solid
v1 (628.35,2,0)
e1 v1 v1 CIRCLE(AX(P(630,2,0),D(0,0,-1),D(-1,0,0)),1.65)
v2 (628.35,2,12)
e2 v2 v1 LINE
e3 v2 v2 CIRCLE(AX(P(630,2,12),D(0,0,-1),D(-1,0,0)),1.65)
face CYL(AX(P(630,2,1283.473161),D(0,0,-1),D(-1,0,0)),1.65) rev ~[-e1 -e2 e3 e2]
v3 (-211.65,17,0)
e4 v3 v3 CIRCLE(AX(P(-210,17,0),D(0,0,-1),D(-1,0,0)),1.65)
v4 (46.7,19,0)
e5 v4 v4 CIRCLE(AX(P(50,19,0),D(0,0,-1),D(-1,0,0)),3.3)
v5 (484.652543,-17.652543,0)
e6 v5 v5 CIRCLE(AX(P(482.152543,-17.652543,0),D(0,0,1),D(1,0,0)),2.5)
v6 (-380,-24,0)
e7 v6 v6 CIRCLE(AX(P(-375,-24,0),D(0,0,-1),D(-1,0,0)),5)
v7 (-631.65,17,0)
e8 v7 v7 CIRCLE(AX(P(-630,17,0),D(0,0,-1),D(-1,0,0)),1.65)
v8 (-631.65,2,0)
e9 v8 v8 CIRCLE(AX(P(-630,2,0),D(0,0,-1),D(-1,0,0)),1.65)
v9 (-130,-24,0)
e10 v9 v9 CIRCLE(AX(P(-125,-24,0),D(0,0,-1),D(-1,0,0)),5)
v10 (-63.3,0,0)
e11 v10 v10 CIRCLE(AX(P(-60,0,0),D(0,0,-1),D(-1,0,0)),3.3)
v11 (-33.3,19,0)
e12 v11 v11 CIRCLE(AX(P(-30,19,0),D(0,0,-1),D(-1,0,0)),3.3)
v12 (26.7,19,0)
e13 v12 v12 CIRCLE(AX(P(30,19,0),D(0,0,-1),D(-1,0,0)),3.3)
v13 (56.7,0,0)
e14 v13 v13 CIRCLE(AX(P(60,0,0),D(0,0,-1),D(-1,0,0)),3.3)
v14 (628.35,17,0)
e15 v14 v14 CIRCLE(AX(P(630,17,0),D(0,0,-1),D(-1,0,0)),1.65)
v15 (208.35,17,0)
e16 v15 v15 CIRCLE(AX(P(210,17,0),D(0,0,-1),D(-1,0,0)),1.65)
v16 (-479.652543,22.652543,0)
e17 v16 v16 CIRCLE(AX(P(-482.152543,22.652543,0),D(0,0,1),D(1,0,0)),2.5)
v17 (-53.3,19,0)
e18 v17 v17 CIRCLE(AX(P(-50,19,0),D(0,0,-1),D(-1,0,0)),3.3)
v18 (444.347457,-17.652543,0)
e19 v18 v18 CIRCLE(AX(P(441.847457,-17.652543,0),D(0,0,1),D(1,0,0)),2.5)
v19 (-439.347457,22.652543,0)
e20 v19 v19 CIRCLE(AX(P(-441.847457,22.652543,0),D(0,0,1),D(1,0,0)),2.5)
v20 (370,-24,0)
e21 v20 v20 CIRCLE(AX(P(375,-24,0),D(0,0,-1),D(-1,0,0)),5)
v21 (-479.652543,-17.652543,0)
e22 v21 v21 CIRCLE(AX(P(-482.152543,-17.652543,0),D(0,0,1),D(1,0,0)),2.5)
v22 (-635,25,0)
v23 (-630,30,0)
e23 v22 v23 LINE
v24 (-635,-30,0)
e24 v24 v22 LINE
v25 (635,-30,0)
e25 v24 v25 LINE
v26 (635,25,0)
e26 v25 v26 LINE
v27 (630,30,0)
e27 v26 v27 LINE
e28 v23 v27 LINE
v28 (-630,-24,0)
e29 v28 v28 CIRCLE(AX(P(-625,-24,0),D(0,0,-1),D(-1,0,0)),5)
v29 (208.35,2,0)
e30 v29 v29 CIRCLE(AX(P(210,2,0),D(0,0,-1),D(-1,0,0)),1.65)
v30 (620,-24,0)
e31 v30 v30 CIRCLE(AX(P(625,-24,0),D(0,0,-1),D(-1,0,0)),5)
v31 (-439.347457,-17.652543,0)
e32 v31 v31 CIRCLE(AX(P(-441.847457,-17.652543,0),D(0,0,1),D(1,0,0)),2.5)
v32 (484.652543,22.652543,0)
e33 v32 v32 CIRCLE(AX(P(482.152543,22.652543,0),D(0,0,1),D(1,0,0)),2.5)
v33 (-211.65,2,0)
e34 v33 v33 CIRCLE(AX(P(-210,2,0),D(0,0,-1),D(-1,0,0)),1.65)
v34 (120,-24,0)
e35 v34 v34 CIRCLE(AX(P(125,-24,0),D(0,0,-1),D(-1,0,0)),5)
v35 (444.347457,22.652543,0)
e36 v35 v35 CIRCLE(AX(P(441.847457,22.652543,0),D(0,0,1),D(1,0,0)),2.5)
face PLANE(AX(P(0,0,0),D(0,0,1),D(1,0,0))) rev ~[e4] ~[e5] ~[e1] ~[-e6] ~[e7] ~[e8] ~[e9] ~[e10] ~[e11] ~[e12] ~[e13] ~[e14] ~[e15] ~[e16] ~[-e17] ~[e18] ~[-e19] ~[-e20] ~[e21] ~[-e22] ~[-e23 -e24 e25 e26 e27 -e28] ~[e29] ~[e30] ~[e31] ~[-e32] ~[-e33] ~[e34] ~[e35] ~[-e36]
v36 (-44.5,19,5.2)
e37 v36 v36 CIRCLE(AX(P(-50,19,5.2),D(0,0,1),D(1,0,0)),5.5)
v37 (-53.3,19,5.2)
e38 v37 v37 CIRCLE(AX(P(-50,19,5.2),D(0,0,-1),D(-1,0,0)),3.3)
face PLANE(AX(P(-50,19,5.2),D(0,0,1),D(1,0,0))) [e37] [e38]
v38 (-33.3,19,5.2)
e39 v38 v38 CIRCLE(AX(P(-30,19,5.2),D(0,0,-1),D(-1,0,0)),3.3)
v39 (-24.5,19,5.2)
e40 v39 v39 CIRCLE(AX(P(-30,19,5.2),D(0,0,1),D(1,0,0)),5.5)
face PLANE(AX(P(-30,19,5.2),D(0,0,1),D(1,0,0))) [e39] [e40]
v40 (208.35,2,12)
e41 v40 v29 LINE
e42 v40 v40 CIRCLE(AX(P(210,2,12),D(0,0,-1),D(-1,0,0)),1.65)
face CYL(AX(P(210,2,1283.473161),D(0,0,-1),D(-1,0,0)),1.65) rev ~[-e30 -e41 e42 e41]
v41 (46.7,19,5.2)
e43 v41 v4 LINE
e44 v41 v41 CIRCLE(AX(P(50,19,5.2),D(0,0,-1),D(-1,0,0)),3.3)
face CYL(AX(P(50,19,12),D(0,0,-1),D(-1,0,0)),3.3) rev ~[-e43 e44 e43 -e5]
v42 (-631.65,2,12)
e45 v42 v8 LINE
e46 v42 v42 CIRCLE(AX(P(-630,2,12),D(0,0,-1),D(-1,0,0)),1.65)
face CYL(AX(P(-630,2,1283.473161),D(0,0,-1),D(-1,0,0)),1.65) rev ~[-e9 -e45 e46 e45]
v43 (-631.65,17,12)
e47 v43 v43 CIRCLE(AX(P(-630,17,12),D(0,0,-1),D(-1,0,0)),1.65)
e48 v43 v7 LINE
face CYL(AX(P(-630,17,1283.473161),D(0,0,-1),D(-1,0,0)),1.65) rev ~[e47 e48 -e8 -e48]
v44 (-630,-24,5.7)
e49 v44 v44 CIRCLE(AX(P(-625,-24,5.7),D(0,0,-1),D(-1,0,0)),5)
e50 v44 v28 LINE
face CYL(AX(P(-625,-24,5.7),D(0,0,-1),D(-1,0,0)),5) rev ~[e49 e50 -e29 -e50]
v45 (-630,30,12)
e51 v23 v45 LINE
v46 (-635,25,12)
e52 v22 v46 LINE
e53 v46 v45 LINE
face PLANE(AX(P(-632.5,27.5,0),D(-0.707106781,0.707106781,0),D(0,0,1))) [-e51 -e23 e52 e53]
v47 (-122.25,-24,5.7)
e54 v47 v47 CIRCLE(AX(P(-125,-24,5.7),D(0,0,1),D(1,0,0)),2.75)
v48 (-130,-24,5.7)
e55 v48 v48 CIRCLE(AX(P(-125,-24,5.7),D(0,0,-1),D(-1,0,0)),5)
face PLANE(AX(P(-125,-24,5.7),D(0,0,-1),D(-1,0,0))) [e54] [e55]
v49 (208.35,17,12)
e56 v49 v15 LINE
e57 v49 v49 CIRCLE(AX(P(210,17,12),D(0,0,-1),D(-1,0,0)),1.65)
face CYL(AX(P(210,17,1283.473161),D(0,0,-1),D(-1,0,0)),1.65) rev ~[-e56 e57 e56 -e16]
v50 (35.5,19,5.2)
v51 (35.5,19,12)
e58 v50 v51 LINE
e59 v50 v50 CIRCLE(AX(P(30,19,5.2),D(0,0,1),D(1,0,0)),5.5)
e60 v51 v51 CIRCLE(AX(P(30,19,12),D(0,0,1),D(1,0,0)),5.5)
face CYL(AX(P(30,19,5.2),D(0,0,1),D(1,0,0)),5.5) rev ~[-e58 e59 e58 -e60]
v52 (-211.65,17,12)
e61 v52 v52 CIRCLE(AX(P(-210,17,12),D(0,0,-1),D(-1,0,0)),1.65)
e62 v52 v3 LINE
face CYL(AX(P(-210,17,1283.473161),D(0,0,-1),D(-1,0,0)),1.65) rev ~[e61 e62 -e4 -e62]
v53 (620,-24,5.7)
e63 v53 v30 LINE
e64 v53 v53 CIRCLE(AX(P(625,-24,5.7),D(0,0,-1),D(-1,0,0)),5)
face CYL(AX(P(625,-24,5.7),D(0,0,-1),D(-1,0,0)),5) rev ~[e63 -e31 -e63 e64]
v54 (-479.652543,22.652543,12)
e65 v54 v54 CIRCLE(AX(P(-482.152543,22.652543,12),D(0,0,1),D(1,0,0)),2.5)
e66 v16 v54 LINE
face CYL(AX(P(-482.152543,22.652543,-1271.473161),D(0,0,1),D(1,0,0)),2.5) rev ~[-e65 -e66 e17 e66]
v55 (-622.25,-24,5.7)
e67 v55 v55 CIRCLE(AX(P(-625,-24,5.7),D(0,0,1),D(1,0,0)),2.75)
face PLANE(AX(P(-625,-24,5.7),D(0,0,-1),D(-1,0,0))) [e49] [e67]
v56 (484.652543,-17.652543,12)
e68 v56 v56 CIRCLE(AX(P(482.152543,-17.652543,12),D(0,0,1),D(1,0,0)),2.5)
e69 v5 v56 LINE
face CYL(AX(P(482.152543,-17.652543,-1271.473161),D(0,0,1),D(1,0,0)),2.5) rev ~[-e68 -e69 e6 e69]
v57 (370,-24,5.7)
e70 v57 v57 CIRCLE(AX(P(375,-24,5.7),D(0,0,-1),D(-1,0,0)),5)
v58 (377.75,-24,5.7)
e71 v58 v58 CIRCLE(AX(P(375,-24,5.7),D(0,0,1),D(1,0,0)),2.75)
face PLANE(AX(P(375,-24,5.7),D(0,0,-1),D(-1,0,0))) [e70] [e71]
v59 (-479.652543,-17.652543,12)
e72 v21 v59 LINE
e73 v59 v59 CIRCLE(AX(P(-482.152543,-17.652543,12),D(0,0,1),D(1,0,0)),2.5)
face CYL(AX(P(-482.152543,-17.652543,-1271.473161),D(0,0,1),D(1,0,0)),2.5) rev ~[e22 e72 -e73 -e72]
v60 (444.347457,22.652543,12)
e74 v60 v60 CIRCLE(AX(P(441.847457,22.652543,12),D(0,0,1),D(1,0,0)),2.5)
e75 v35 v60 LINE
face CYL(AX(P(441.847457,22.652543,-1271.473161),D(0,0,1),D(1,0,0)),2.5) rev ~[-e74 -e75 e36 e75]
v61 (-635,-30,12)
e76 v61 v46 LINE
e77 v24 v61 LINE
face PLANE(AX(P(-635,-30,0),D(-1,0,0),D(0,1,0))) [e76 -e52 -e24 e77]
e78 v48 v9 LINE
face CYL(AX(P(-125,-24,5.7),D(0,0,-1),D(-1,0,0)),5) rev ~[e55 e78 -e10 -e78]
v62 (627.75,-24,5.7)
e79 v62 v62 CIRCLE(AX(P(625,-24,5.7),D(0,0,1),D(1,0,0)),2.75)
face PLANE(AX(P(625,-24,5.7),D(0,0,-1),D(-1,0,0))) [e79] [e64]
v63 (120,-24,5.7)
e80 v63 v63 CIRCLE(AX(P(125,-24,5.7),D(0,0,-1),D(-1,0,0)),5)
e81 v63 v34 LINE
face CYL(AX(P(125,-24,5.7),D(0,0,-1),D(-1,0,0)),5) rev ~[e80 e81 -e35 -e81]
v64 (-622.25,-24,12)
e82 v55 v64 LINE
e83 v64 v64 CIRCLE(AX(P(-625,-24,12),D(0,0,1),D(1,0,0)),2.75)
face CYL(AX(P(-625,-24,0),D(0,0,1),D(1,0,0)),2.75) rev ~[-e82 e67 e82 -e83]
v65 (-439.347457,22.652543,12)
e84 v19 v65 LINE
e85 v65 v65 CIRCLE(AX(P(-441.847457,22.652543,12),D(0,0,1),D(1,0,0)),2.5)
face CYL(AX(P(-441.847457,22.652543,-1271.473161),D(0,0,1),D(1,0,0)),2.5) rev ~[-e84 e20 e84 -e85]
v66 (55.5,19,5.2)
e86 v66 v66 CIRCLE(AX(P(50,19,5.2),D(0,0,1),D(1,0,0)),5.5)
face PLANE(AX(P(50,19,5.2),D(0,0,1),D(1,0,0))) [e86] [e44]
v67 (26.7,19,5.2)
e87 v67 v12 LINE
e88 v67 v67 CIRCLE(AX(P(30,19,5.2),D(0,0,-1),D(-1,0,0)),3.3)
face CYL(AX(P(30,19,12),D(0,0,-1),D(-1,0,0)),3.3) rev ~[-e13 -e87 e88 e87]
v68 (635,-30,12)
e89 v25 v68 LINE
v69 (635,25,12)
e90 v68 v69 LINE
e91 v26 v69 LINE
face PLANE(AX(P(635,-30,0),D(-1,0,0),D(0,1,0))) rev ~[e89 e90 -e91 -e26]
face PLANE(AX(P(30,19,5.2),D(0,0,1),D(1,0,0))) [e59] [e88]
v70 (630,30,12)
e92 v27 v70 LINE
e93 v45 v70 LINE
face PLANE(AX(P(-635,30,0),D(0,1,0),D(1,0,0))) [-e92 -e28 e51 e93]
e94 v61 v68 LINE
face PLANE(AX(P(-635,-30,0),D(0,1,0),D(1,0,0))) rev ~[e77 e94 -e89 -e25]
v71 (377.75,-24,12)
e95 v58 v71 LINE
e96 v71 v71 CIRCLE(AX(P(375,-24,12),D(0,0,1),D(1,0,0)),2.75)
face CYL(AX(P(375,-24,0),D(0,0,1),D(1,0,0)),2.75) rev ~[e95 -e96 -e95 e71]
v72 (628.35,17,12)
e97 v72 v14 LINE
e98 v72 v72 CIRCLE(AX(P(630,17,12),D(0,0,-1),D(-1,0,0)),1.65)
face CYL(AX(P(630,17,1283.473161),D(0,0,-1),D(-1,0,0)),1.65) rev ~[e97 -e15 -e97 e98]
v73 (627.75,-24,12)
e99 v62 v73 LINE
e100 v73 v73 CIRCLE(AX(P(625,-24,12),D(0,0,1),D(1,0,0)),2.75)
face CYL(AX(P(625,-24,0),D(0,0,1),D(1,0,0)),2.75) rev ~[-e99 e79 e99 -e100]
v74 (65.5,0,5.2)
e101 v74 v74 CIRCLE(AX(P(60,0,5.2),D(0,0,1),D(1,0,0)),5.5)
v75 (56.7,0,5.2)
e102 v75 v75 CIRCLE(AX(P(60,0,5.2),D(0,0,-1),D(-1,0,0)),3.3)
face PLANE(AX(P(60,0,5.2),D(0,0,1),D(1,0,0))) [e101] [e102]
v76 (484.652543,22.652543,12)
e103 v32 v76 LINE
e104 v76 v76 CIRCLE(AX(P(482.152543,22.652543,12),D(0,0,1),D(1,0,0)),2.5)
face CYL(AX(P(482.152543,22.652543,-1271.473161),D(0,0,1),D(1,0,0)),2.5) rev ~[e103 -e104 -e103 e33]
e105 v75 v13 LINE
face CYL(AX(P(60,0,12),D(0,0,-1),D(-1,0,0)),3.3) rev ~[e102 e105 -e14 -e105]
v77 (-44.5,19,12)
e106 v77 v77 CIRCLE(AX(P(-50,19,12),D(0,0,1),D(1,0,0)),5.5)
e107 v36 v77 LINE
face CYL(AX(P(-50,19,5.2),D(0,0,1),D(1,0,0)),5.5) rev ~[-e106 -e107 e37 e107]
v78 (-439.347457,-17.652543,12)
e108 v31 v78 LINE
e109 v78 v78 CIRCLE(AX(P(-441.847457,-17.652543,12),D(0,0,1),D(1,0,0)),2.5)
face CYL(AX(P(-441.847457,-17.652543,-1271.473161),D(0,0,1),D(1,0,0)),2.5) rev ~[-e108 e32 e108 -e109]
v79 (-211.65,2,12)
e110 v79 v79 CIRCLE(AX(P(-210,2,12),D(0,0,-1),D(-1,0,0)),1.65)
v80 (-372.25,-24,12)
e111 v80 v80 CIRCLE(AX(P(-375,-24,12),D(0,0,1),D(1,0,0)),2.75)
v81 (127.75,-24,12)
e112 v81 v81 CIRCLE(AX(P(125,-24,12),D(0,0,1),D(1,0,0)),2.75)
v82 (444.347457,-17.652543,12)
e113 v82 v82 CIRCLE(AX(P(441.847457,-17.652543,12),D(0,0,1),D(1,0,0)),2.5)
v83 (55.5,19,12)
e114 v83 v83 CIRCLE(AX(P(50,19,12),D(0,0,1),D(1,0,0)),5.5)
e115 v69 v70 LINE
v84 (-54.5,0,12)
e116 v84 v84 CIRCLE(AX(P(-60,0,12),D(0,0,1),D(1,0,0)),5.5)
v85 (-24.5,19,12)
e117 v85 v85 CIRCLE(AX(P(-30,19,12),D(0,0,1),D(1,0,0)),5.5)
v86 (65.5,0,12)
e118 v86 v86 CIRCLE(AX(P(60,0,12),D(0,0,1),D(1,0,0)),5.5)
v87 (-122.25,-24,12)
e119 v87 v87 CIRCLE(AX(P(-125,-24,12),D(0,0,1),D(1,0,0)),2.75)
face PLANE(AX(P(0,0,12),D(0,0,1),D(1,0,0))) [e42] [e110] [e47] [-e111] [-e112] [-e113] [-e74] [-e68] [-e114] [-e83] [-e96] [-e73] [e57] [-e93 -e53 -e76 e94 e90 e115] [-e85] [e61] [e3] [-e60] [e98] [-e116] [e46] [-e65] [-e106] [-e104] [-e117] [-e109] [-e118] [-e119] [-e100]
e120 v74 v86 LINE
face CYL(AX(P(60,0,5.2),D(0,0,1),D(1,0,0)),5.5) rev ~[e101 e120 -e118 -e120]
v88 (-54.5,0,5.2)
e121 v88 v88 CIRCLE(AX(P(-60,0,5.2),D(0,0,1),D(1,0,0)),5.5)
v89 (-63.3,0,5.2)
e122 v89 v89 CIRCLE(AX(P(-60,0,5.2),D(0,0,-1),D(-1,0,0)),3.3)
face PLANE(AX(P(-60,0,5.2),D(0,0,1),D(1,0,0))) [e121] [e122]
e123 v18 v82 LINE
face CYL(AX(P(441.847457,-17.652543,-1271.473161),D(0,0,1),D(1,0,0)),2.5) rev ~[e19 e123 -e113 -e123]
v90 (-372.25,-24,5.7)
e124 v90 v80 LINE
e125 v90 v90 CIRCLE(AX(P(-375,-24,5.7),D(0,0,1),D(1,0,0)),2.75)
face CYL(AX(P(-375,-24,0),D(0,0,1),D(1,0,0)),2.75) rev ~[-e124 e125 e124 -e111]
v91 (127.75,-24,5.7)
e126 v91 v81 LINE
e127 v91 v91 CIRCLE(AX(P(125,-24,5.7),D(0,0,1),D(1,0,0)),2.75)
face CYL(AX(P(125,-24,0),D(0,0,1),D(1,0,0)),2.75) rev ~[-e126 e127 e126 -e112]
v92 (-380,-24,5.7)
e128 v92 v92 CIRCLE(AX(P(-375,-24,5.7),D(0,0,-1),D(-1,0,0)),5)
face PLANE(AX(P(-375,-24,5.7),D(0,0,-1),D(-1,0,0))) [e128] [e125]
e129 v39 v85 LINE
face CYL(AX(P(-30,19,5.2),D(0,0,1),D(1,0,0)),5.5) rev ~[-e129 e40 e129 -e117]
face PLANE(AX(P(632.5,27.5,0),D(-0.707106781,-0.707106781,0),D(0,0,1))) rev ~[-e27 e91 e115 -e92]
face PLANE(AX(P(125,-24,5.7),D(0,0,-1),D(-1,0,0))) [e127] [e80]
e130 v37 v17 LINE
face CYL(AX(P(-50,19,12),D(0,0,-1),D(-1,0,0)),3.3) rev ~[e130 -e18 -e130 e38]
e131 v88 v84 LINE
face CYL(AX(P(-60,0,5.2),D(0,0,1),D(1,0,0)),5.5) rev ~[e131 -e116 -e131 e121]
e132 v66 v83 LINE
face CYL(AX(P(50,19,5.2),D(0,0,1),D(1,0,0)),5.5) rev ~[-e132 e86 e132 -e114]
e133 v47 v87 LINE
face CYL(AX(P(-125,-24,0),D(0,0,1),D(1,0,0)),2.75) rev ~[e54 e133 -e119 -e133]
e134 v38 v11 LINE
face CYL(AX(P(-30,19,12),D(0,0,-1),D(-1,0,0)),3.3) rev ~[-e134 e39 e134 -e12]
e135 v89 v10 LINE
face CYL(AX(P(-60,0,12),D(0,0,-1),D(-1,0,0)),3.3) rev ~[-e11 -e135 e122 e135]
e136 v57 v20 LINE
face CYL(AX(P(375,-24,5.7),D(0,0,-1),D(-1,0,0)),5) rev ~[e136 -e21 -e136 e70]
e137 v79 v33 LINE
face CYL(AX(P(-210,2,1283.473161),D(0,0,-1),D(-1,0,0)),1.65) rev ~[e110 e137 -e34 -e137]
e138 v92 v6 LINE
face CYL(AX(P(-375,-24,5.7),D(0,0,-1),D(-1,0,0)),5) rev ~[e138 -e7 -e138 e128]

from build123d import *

# Parameters (mm, degrees)
SKETCH_1_W                = 1270
SKETCH_1_H                = 60
EXTRUDE_1_DEPTH           = 12
CHAMFER_1_SIZE            = 5
HOLE_WIZARD_1_D           = 5.5
HOLE_WIZARD_1_CBORE_D     = 10
HOLE_WIZARD_1_CBORE_DEPTH = 5.7
HOLE_WIZARD_M6_1_D        = 5
HOLE_WIZARD_M4_1_D        = 3.3
HOLE_WIZARD_2_D           = 6.6
HOLE_WIZARD_2_CBORE_D     = 11
HOLE_WIZARD_2_CBORE_DEPTH = 6.8


with BuildPart() as part:
    # 草图1 → 凸台-拉伸1 (new body)
    with BuildSketch(Plane.XY):
        Rectangle(SKETCH_1_W, SKETCH_1_H)
    extrude(amount=EXTRUDE_1_DEPTH)

    # 倒角1
    chamfer_1_edges = [part.edges().sort_by_distance(p)[0] for p in [
        (-635, 30, 6),
        (635, 30, 6),
    ]]
    chamfer(chamfer_1_edges, length=CHAMFER_1_SIZE)

    # 打孔尺寸(%根据)内六角圆柱头螺钉的类型1 (through all)
    with Locations(Plane(origin=(0, 0, 0), x_dir=(-1, 0, 0), z_dir=(0, 0, -1))):
        with Locations((-625, -24), (-375, -24), (-125, -24), (125, -24), (375, -24), (625, -24)):
            CounterBoreHole(HOLE_WIZARD_1_D / 2, HOLE_WIZARD_1_CBORE_D / 2, HOLE_WIZARD_1_CBORE_DEPTH)

    # M6 螺纹孔1 (through all)
    with Locations(Plane(origin=(0, 0, 0), x_dir=(-1, 0, 0), z_dir=(0, 0, -1))):
        with Locations((-482.152543264, 22.652543264), (-441.847456736, 22.652543264), (-441.847456736, -17.652543264), (-482.152543264, -17.652543264), (482.152543264, -17.652543264), (441.847456736, -17.652543264), (441.847456736, 22.652543264), (482.152543264, 22.652543264)):
            Hole(HOLE_WIZARD_M6_1_D / 2)

    # M4 螺纹孔1 (through all)
    with Locations(Plane.XY.offset(12)):
        with Locations((-630, 17), (-630, 2), (630, 2), (630, 17), (-210, 17), (-210, 2), (210, 2), (210, 17)):
            Hole(HOLE_WIZARD_M4_1_D / 2)

    # 打孔尺寸(%根据)内六角圆柱头螺钉的类型2 (through all)
    with Locations(Plane.XY.offset(12)):
        with Locations((-60, 0), (-50, 19), (-30, 19), (30, 19), (50, 19), (60, 0)):
            CounterBoreHole(HOLE_WIZARD_2_D / 2, HOLE_WIZARD_2_CBORE_D / 2, HOLE_WIZARD_2_CBORE_DEPTH)


solid = part.part
